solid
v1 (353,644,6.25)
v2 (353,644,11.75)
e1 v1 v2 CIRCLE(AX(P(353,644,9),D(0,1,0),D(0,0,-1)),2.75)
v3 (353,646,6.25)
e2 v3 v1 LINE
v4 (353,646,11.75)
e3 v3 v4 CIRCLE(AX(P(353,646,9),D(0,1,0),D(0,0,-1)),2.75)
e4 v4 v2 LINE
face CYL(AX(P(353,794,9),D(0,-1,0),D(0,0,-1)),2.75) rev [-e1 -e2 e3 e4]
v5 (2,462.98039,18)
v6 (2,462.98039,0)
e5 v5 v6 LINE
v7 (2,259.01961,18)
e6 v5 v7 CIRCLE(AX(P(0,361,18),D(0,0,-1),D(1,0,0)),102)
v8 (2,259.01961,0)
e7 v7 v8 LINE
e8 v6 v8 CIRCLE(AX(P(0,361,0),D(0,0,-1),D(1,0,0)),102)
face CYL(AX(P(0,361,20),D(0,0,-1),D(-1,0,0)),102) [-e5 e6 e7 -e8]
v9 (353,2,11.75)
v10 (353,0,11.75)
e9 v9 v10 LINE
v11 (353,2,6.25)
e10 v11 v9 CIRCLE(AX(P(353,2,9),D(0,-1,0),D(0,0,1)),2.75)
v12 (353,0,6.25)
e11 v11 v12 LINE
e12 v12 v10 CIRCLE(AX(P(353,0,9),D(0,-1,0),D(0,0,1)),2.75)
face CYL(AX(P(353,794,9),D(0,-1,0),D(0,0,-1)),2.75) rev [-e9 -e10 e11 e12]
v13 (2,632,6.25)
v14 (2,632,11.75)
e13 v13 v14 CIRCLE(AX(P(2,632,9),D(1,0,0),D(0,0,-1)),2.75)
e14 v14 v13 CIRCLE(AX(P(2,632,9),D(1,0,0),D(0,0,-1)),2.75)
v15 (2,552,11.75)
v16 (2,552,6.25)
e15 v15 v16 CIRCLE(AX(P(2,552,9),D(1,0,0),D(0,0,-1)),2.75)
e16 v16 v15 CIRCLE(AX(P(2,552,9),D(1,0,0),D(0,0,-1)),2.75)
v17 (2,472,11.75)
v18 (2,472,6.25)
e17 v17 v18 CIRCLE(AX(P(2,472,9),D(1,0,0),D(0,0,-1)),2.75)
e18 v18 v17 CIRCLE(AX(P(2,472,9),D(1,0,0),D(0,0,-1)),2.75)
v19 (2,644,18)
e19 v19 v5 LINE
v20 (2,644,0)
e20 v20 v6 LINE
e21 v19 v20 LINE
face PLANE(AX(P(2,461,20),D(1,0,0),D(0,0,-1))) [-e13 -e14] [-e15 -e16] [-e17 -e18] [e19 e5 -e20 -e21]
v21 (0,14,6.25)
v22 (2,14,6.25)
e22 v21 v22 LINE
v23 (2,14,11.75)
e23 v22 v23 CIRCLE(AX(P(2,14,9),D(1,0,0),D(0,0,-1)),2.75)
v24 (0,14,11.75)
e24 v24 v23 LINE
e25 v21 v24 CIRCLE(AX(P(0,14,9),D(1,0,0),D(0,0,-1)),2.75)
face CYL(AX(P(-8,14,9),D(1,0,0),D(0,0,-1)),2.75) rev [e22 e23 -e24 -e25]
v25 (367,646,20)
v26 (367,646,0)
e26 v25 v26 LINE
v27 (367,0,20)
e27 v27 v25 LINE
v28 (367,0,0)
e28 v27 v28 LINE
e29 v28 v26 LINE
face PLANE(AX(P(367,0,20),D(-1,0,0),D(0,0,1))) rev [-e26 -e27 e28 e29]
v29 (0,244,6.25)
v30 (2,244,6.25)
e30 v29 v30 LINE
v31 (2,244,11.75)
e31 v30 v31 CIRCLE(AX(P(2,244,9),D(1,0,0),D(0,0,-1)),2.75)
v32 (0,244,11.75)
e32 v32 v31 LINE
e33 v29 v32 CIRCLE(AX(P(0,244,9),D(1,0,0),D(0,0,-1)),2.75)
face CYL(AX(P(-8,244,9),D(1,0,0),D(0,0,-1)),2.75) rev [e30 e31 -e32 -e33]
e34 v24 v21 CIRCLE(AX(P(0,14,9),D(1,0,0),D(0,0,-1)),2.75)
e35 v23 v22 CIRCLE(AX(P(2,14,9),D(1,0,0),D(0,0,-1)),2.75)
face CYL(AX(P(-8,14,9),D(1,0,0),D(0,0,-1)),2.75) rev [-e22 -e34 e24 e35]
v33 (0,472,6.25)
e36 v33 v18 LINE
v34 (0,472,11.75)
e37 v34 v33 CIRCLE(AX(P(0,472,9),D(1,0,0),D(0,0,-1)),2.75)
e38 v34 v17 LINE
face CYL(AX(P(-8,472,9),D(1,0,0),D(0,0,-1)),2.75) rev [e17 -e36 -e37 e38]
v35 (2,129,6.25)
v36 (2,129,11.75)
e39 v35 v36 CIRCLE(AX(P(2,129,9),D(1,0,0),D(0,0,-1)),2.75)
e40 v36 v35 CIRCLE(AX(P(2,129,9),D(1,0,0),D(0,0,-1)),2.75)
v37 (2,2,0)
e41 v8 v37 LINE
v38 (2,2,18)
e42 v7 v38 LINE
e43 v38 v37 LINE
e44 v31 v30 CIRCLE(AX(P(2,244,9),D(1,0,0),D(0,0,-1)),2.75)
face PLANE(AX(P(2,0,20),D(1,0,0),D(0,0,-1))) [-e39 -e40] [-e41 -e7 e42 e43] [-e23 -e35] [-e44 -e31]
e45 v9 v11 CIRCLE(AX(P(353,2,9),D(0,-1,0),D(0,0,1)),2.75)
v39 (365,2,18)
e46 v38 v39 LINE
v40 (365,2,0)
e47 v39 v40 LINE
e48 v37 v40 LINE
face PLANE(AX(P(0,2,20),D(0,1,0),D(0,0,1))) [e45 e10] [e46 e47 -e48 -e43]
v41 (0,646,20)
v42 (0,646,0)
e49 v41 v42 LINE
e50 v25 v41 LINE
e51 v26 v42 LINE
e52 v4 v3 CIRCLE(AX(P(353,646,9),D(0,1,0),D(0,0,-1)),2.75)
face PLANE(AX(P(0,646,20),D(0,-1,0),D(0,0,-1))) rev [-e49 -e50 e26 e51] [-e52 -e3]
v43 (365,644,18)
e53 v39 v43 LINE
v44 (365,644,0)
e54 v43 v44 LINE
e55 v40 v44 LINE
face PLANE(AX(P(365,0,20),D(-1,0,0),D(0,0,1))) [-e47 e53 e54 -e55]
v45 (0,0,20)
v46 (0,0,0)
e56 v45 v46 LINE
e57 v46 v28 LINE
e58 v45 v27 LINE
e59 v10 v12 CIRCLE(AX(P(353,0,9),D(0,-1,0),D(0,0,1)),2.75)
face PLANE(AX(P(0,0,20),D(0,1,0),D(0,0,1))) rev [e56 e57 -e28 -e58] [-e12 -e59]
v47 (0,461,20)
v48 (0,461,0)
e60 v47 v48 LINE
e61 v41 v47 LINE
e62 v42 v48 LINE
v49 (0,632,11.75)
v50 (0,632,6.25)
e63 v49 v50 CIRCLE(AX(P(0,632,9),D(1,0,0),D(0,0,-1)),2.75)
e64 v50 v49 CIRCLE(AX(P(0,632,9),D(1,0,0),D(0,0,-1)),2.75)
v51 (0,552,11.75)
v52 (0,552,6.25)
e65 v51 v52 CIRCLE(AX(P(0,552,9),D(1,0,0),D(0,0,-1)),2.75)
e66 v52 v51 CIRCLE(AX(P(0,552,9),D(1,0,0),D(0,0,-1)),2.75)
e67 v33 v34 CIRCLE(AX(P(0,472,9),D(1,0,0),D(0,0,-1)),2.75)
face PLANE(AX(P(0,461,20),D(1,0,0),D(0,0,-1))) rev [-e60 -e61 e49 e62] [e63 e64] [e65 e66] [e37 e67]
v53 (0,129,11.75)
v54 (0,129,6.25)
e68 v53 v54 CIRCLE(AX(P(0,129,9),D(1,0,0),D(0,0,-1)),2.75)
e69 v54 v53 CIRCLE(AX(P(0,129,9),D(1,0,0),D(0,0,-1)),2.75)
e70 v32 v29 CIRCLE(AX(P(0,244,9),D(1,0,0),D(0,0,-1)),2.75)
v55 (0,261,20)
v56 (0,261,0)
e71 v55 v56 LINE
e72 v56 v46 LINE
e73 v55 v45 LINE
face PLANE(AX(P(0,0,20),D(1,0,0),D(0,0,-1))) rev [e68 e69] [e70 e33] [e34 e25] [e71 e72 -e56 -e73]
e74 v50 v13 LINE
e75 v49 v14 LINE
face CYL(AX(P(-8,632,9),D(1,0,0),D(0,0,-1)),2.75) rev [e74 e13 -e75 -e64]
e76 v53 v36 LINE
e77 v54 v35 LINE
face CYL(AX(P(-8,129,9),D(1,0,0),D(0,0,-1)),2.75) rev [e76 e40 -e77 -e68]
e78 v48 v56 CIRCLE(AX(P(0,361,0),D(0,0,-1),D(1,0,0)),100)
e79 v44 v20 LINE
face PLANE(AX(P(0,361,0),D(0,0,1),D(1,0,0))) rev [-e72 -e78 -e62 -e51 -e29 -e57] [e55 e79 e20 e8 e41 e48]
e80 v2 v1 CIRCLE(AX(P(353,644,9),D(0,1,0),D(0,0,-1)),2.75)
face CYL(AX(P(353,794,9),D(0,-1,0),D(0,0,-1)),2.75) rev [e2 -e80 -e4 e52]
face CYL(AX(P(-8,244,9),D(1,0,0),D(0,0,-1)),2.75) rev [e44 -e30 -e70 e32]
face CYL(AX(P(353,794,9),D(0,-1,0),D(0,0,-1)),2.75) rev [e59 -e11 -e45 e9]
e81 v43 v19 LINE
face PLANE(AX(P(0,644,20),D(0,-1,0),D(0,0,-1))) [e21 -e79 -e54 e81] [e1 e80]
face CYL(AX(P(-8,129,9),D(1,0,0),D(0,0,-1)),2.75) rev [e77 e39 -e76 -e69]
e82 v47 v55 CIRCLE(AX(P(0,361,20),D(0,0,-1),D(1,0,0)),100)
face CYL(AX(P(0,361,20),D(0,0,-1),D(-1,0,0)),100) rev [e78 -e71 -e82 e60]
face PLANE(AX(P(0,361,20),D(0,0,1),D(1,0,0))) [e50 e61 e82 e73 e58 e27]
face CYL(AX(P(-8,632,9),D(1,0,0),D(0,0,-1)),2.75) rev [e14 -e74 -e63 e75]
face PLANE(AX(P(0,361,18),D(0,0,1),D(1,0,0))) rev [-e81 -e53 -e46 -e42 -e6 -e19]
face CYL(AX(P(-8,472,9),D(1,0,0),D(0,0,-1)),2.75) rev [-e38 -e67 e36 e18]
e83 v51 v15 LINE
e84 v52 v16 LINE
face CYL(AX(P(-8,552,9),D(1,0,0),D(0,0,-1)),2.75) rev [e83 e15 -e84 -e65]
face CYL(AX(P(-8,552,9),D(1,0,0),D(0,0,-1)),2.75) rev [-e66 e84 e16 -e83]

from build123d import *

# Parameters (mm, degrees)
EXTRUDE_1_DEPTH          = 20
SHELL_1_T                = -2
CUT_EXTRUDE_1_DEPTH      = 792
CUT_EXTRUDE_1_DEPTH_BACK = 76
SKETCH_2_R               = 2.75
SKETCH_3_R               = 2.75
CUT_EXTRUDE_2_DEPTH      = 10


with BuildPart() as part:
    # 草图1 → 凸台-拉伸1 (new body)
    with BuildSketch(Plane.XY):
        with BuildLine():
            Line((0, 461), (0, 646))
            Line((0, 646), (367, 646))
            Line((367, 646), (367, 0))
            Line((367, 0), (0, 0))
            Line((0, 0), (0, 261))
            ThreePointArc((0, 261), (100, 361), (0, 461))
        make_face()
    extrude(amount=EXTRUDE_1_DEPTH)

    # 抽壳1
    shell_1_openings = [part.faces().sort_by_distance(p)[0] for p in [
        (193.509053572, 320.303646747, 0),
    ]]
    offset(amount=SHELL_1_T, openings=shell_1_openings, kind=Kind.INTERSECTION)

    # 草图2 → 切除-拉伸1 (cut, two sides: drawn at the far end of the back side and taken through both)
    with BuildSketch(Plane(origin=(0, 2, 0), x_dir=(1, 0, 0), z_dir=(0, 1, 0)).offset(-CUT_EXTRUDE_1_DEPTH_BACK)):
        with Locations(Location((353, -9, 0), (0, 0, 90))):
            Circle(SKETCH_2_R)
    extrude(amount=CUT_EXTRUDE_1_DEPTH + CUT_EXTRUDE_1_DEPTH_BACK, mode=Mode.SUBTRACT)

    # 草图3 → 切除-拉伸2 (cut)
    with BuildSketch(Plane(origin=(2, 0, 0), x_dir=(0, 0, -1), z_dir=(1, 0, 0))):
        with Locations((-9, 632)):
            Circle(SKETCH_3_R)
        with Locations((-9, 552)):
            Circle(SKETCH_3_R)
        with Locations((-9, 472)):
            Circle(SKETCH_3_R)
        with Locations((-9, 14)):
            Circle(SKETCH_3_R)
        with Locations((-9, 129)):
            Circle(SKETCH_3_R)
        with Locations((-9, 244)):
            Circle(SKETCH_3_R)
    extrude(amount=-CUT_EXTRUDE_2_DEPTH, mode=Mode.SUBTRACT)


solid = part.part
